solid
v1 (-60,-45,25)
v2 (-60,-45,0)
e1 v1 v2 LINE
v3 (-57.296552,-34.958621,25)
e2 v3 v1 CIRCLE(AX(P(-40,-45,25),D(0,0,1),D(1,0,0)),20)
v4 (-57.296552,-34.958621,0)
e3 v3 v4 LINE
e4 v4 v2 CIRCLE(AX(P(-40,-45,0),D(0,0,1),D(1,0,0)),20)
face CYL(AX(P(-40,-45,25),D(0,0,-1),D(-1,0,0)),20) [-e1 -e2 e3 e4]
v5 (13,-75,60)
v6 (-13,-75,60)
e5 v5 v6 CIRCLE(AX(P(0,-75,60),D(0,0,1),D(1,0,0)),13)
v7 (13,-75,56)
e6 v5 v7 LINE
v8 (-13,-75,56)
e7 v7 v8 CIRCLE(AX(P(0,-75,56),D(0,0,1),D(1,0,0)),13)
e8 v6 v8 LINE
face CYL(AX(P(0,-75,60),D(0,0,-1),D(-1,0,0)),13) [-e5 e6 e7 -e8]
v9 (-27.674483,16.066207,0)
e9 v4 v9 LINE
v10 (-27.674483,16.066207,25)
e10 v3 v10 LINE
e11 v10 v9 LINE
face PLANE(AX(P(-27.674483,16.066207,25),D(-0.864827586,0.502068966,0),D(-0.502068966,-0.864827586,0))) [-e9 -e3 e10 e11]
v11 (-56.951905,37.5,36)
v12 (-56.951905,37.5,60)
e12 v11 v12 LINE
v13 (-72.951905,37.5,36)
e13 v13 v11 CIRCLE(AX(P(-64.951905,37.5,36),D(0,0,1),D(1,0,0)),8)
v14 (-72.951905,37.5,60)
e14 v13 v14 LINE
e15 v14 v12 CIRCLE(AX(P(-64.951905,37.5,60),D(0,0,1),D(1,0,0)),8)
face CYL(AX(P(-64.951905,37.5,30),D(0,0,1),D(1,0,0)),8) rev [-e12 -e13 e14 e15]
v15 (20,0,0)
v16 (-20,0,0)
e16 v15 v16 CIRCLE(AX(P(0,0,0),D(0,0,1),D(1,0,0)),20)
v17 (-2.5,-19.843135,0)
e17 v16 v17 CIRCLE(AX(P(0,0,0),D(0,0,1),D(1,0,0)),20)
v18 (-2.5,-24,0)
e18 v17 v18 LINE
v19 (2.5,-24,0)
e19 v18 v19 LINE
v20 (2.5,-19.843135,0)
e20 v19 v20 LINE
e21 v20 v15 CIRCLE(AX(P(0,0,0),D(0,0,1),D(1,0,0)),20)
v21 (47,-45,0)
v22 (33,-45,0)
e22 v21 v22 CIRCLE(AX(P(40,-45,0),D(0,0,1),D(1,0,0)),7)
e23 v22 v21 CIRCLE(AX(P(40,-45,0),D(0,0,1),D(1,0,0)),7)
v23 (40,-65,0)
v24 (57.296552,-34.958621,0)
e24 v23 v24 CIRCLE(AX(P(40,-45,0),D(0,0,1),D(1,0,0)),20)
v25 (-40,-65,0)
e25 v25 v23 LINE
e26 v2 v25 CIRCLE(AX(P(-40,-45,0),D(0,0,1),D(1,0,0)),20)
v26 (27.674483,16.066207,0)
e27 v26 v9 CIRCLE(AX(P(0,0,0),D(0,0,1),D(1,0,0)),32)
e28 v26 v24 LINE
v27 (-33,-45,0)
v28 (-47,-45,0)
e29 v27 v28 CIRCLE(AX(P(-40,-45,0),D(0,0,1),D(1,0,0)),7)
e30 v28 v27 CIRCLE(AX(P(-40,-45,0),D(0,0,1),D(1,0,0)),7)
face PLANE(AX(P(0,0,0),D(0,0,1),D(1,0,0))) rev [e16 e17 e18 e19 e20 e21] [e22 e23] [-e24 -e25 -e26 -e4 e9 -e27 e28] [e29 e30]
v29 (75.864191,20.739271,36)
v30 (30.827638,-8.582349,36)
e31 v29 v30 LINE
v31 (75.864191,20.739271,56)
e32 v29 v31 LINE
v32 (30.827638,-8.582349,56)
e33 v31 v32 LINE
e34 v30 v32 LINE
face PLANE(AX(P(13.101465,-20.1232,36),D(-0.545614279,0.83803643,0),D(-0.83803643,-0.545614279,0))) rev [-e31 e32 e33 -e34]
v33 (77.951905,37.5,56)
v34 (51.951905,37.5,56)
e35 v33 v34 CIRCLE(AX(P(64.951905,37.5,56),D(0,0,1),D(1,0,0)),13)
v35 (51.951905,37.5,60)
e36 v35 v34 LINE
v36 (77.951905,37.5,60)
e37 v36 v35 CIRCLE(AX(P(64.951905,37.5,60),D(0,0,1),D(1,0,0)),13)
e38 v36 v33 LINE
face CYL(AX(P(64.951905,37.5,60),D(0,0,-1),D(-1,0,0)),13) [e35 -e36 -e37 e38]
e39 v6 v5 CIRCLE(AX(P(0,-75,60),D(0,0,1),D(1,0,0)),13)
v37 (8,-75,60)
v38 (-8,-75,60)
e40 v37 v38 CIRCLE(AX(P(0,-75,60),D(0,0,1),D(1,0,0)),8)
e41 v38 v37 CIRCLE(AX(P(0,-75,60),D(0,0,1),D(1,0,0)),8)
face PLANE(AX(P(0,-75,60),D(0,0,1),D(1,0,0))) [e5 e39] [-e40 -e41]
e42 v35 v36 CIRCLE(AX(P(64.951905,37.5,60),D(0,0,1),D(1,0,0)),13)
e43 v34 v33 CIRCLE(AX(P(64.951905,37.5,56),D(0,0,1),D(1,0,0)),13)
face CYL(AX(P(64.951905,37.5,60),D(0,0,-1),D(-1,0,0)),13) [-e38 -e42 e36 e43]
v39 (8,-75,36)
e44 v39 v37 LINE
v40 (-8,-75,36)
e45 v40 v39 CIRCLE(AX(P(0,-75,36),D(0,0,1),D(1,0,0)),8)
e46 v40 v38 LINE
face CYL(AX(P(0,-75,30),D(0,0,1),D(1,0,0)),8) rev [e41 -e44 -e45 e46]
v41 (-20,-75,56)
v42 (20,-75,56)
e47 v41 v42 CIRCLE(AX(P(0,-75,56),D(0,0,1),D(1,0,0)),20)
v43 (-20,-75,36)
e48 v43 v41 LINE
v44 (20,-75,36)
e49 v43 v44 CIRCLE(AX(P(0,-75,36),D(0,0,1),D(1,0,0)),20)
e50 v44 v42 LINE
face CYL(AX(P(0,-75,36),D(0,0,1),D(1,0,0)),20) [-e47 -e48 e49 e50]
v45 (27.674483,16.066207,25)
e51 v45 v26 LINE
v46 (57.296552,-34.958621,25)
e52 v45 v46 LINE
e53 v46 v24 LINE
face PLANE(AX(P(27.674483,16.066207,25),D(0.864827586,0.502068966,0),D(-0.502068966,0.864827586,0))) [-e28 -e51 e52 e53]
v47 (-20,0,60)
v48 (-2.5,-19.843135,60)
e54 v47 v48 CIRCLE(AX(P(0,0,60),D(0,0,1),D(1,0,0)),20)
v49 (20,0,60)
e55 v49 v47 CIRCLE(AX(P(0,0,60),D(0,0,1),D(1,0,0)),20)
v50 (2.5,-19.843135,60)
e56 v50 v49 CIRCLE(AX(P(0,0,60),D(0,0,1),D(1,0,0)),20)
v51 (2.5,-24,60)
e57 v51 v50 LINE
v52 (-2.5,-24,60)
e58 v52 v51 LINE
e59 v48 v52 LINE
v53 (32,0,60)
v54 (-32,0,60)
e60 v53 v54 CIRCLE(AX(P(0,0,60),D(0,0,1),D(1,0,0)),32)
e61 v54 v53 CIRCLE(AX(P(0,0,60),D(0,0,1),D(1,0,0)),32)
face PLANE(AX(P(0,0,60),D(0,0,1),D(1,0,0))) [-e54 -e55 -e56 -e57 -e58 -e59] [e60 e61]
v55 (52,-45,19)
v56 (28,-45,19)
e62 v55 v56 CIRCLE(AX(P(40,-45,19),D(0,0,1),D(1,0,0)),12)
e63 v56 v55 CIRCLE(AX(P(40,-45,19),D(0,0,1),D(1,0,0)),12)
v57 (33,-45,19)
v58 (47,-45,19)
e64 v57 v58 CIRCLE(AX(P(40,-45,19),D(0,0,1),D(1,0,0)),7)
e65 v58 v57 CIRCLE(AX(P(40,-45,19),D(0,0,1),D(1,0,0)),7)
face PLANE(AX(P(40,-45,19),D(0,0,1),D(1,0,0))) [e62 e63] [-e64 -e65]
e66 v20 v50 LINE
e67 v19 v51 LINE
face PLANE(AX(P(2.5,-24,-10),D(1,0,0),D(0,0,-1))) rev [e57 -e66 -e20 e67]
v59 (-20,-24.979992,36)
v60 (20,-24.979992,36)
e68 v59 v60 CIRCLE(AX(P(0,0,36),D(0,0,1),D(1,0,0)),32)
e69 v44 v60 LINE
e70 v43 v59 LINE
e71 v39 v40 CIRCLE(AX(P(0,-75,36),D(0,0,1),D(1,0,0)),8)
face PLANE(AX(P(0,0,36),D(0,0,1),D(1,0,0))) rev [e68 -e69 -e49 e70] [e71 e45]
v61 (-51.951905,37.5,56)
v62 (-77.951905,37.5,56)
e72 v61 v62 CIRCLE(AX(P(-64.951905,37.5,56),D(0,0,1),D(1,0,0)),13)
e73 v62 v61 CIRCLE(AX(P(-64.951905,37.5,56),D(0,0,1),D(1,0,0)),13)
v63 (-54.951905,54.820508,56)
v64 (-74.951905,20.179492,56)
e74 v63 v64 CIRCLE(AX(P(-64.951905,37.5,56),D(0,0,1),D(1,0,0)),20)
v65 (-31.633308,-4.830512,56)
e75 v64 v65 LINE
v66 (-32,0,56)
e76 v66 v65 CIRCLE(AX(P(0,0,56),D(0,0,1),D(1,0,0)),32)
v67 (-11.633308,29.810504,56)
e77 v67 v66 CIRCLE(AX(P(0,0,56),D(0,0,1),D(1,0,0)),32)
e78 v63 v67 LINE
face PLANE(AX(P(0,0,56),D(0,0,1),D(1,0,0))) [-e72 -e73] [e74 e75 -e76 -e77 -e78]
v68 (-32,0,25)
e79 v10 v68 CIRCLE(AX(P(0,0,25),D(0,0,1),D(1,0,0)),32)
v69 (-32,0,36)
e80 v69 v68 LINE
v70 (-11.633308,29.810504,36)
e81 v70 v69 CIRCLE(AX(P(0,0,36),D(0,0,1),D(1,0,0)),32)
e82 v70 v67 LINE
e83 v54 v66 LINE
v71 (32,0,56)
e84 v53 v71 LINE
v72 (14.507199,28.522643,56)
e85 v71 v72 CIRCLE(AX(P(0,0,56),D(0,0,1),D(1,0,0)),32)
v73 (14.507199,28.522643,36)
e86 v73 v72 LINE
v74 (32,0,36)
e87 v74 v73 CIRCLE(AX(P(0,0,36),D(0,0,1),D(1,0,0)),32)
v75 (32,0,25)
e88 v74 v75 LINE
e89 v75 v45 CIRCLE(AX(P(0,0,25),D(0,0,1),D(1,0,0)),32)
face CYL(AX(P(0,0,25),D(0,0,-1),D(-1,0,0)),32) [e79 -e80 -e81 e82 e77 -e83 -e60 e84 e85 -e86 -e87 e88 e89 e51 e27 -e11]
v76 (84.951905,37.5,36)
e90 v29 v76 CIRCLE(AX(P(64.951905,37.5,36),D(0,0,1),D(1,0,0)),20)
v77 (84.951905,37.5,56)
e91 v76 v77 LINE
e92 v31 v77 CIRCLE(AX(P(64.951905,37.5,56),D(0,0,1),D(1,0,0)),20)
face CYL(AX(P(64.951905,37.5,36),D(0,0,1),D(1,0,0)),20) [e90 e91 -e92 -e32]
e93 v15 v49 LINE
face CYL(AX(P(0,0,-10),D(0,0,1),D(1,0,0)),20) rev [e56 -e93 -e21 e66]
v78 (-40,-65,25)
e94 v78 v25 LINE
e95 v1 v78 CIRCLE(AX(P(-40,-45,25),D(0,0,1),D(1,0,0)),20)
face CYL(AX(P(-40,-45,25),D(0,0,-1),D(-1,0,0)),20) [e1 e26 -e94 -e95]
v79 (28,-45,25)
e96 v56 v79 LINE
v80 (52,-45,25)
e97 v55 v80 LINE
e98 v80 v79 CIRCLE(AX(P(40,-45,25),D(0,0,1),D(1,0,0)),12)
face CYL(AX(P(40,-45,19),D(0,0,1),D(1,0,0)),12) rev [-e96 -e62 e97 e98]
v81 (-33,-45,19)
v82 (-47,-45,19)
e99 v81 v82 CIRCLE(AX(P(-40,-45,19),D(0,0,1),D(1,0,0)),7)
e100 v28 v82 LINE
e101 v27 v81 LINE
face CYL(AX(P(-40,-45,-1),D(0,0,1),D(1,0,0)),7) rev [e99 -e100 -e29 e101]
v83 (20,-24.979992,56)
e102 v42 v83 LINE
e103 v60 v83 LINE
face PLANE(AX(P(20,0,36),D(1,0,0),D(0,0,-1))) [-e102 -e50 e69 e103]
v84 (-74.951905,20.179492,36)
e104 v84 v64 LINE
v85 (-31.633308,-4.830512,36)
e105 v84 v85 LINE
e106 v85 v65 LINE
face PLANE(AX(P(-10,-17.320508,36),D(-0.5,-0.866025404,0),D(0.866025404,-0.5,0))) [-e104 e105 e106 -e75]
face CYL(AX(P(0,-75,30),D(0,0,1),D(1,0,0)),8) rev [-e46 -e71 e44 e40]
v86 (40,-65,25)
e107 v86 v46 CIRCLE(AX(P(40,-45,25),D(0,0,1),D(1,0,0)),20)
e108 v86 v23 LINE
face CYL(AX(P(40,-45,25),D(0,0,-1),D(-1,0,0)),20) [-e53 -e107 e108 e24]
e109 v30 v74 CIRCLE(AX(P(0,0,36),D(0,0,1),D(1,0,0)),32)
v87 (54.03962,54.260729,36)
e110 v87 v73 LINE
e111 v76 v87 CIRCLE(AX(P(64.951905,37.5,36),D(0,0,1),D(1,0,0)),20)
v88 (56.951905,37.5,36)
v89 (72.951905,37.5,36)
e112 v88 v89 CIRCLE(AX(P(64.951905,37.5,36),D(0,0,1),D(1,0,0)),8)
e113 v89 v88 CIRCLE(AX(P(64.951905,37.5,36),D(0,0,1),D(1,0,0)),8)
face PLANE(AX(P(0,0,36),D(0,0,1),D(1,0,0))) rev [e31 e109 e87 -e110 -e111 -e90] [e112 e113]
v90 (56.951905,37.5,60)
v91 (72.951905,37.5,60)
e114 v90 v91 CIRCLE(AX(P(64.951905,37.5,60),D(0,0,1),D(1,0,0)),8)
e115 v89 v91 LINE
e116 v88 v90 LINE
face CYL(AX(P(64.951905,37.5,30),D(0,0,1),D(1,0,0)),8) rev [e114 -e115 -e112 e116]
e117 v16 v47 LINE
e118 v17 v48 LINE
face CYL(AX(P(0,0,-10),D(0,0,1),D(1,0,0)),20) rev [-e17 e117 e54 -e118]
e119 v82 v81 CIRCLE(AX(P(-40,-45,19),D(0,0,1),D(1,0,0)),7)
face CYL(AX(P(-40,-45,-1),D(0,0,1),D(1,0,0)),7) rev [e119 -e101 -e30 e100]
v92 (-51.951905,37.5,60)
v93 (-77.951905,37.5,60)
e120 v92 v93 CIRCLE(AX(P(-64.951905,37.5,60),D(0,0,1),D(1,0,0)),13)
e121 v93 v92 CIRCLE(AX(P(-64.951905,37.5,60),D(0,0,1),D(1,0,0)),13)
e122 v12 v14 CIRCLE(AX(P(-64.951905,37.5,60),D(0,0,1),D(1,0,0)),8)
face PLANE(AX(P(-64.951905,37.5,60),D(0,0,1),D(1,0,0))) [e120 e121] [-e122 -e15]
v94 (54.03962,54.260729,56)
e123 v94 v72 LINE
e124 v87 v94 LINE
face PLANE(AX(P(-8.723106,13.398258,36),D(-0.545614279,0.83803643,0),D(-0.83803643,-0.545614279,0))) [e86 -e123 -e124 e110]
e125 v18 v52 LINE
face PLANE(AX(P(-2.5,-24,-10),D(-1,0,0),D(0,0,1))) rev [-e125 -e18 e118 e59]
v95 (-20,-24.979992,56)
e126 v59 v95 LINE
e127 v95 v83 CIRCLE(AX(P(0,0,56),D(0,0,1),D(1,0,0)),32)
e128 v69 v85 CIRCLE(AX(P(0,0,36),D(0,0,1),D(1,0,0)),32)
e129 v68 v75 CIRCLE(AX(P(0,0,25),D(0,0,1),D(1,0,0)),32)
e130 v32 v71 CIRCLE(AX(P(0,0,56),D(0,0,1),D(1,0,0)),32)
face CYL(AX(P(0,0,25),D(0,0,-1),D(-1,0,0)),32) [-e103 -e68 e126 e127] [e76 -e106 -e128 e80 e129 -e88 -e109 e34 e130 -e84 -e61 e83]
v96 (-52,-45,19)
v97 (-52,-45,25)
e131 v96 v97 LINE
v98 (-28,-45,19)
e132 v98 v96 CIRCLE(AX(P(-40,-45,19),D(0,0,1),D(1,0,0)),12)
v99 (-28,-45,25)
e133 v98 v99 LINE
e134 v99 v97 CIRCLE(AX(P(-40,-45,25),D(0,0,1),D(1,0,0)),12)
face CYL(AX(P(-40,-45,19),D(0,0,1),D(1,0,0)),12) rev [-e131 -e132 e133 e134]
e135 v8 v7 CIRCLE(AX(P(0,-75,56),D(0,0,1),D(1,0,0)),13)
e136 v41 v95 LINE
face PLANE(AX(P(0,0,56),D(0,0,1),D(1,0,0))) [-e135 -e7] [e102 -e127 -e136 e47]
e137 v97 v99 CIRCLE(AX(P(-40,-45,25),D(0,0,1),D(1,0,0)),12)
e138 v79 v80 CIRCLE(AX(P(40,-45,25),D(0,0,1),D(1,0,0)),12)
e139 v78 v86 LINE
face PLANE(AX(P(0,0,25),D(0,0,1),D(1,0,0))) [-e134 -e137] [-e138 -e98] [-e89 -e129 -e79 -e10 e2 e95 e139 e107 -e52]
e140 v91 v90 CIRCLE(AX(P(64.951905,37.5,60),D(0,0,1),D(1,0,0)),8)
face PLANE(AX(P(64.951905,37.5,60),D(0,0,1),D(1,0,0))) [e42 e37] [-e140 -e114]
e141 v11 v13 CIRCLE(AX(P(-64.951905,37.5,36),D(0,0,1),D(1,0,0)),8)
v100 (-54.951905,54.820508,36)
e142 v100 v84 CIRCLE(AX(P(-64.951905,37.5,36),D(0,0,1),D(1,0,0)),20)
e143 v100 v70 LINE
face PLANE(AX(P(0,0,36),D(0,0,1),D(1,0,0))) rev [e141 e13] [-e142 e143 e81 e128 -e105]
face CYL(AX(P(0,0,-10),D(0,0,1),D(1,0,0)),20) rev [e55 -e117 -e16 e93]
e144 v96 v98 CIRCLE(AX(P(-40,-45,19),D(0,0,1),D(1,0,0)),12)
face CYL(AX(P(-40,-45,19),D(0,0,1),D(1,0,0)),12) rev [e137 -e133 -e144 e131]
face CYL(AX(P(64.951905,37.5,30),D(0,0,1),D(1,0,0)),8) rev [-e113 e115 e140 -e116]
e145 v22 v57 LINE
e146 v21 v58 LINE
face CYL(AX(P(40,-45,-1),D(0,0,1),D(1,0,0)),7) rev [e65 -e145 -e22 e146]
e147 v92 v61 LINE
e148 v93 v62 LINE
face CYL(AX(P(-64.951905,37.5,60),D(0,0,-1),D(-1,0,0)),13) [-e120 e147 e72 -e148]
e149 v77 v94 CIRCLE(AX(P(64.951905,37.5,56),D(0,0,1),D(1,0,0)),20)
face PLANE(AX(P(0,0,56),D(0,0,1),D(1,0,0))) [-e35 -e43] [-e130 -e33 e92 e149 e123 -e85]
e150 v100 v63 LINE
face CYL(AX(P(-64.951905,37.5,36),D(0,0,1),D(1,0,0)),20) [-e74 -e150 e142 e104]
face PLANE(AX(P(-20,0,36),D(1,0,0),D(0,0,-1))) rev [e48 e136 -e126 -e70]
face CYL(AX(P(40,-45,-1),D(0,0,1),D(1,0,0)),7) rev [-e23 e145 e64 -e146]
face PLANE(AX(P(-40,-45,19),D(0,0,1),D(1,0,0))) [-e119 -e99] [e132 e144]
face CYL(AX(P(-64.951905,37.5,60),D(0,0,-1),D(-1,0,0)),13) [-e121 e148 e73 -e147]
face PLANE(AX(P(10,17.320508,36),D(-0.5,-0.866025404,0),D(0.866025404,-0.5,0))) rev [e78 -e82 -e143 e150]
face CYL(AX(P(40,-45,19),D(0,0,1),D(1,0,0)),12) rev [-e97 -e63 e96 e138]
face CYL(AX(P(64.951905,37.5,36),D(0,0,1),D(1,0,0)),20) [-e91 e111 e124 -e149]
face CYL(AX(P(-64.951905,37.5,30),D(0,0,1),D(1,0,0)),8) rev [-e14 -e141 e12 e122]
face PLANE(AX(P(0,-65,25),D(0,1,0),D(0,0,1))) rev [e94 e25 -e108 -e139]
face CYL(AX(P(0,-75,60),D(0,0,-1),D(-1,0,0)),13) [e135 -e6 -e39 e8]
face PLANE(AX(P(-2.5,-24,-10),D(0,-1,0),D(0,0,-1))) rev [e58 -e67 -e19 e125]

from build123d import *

# Parameters (mm, degrees)
LOWER_ARMS_25MM_DEPTH                 = 25
HUB_BOSS_SKETCH_32_R                  = 32
HUB_BOSS_32_DEPTH                     = 31
UPPER_START                           = -20
UPPER_ARMS_20MM_DEPTH                 = 20
HUB_COLLAR_SKETCH_32_R                = 32
HUB_COLLAR_32X4_DEPTH                 = 4
KEYED_HUB_BORE_DEPTH                  = 70
UPPER_ARM_PADS_SKETCH_3X_13_R         = 13
UPPER_ARM_PADS_3X_13_DEPTH            = 4
UPPER_ARM_HOLES_SKETCH_3X_8_R         = 8
UPPER_ARM_HOLES_3X_8_DEPTH            = 30
LOWER_ARM_COUNTERBORES_SKETCH_2X_12_R = 12
LOWER_ARM_COUNTERBORES_2X_12_DEPTH    = 6
LOWER_ARM_HOLES_SKETCH_2X_7_R         = 7
LOWER_ARM_HOLES_2X_7_DEPTH            = 20


with BuildPart() as part:
    # Lower Arms Profile → Lower Arms 25mm (new body)
    with BuildSketch(Plane.XY):
        with BuildLine():
            Line((-57.296551724, -34.95862069), (-27.674482759, 16.066206897))
            ThreePointArc((-27.674482759, 16.066206897), (0, 32), (27.674482759, 16.066206897))
            Line((27.674482759, 16.066206897), (57.296551724, -34.95862069))
            ThreePointArc((57.296551724, -34.95862069), (57.332449137, -54.979288897), (40, -65))
            Line((40, -65), (-40, -65))
            ThreePointArc((-40, -65), (-57.332449137, -54.979288897), (-57.296551724, -34.95862069))
        make_face()
    extrude(amount=LOWER_ARMS_25MM_DEPTH)

    # Hub Boss Sketch Ø32 → Hub Boss Ø32 (add)
    with BuildSketch(Plane.XY.offset(25)):
        with Locations(Location((0, 0, 0), (0, 0, 149.863023681))):
            Circle(HUB_BOSS_SKETCH_32_R)
    extrude(amount=HUB_BOSS_32_DEPTH)

    # Upper Arms Profile → Upper Arms 20mm (add)
    with BuildSketch(Plane.XY.offset(56).offset(UPPER_START)):
        with BuildLine():
            Line((-20, -24.979991994), (-20, -75))
            ThreePointArc((-20, -75), (0, -95), (20, -75))
            Line((20, -75), (20, -24.979991994))
            ThreePointArc((20, -24.979991994), (0, -32), (-20, -24.979991994))
        make_face()
        with BuildLine():
            ThreePointArc((-54.951905284, 54.820508076), (-82.27241336, 47.5), (-74.951905284, 20.179491924))
            Line((-74.951905284, 20.179491924), (-31.633307653, -4.830512079))
            ThreePointArc((-31.633307653, -4.830512079), (-27.712812921, 16), (-11.633307653, 29.810504072))
            Line((-11.633307653, 29.810504072), (-54.951905284, 54.820508076))
        make_face()
        with BuildLine():
            ThreePointArc((75.864190859, 20.73927139), (81.712633894, 48.412285575), (54.039619709, 54.26072861))
            Line((54.039619709, 54.26072861), (14.507199018, 28.522643227))
            ThreePointArc((14.507199018, 28.522643227), (29.291756215, 12.883827763), (30.827638328, -8.582349045))
            Line((30.827638328, -8.582349045), (75.864190859, 20.73927139))
        make_face()
    extrude(amount=UPPER_ARMS_20MM_DEPTH)

    # Hub Collar Sketch Ø32 → Hub Collar Ø32x4 (add)
    with BuildSketch(Plane.XY.offset(56)):
        with Locations(Location((0, 0, 0), (0, 0, 149.863023681))):
            Circle(HUB_COLLAR_SKETCH_32_R)
    extrude(amount=HUB_COLLAR_32X4_DEPTH)

    # Keyed Bore Sketch → Keyed Hub Bore (cut)
    with BuildSketch(Plane.XY.offset(60)):
        with BuildLine():
            Line((-2.5, -24), (2.5, -24))
            Line((2.5, -24), (2.5, -19.843134833))
            ThreePointArc((2.5, -19.843134833), (0, 20), (-2.5, -19.843134833))
            Line((-2.5, -19.843134833), (-2.5, -24))
        make_face()
    extrude(amount=-KEYED_HUB_BORE_DEPTH, mode=Mode.SUBTRACT)

    # Upper Arm Pads Sketch 3xØ13 → Upper Arm Pads 3xØ13 (add)
    with BuildSketch(Plane.XY.offset(56)):
        with Locations((-64.951905284, 37.5)):
            Circle(UPPER_ARM_PADS_SKETCH_3X_13_R)
        with Locations((64.951905284, 37.5)):
            Circle(UPPER_ARM_PADS_SKETCH_3X_13_R)
        with Locations((0, -75)):
            Circle(UPPER_ARM_PADS_SKETCH_3X_13_R)
    extrude(amount=UPPER_ARM_PADS_3X_13_DEPTH)

    # Upper Arm Holes Sketch 3xØ8 → Upper Arm Holes 3xØ8 (cut)
    with BuildSketch(Plane.XY.offset(60)):
        with Locations((-64.951905284, 37.5)):
            Circle(UPPER_ARM_HOLES_SKETCH_3X_8_R)
        with Locations((64.951905284, 37.5)):
            Circle(UPPER_ARM_HOLES_SKETCH_3X_8_R)
        with Locations((0, -75)):
            Circle(UPPER_ARM_HOLES_SKETCH_3X_8_R)
    extrude(amount=-UPPER_ARM_HOLES_3X_8_DEPTH, mode=Mode.SUBTRACT)

    # Lower Arm Counterbores Sketch 2xØ12 → Lower Arm Counterbores 2xØ12 (cut)
    with BuildSketch(Plane.XY.offset(25)):
        with Locations((-40, -45)):
            Circle(LOWER_ARM_COUNTERBORES_SKETCH_2X_12_R)
        with Locations((40, -45)):
            Circle(LOWER_ARM_COUNTERBORES_SKETCH_2X_12_R)
    extrude(amount=-LOWER_ARM_COUNTERBORES_2X_12_DEPTH, mode=Mode.SUBTRACT)

    # Lower Arm Holes Sketch 2xØ7 → Lower Arm Holes 2xØ7 (cut)
    with BuildSketch(Plane.XY.offset(19)):
        with Locations((-40, -45)):
            Circle(LOWER_ARM_HOLES_SKETCH_2X_7_R)
        with Locations((40, -45)):
            Circle(LOWER_ARM_HOLES_SKETCH_2X_7_R)
    extrude(amount=-LOWER_ARM_HOLES_2X_7_DEPTH, mode=Mode.SUBTRACT)


solid = part.part
